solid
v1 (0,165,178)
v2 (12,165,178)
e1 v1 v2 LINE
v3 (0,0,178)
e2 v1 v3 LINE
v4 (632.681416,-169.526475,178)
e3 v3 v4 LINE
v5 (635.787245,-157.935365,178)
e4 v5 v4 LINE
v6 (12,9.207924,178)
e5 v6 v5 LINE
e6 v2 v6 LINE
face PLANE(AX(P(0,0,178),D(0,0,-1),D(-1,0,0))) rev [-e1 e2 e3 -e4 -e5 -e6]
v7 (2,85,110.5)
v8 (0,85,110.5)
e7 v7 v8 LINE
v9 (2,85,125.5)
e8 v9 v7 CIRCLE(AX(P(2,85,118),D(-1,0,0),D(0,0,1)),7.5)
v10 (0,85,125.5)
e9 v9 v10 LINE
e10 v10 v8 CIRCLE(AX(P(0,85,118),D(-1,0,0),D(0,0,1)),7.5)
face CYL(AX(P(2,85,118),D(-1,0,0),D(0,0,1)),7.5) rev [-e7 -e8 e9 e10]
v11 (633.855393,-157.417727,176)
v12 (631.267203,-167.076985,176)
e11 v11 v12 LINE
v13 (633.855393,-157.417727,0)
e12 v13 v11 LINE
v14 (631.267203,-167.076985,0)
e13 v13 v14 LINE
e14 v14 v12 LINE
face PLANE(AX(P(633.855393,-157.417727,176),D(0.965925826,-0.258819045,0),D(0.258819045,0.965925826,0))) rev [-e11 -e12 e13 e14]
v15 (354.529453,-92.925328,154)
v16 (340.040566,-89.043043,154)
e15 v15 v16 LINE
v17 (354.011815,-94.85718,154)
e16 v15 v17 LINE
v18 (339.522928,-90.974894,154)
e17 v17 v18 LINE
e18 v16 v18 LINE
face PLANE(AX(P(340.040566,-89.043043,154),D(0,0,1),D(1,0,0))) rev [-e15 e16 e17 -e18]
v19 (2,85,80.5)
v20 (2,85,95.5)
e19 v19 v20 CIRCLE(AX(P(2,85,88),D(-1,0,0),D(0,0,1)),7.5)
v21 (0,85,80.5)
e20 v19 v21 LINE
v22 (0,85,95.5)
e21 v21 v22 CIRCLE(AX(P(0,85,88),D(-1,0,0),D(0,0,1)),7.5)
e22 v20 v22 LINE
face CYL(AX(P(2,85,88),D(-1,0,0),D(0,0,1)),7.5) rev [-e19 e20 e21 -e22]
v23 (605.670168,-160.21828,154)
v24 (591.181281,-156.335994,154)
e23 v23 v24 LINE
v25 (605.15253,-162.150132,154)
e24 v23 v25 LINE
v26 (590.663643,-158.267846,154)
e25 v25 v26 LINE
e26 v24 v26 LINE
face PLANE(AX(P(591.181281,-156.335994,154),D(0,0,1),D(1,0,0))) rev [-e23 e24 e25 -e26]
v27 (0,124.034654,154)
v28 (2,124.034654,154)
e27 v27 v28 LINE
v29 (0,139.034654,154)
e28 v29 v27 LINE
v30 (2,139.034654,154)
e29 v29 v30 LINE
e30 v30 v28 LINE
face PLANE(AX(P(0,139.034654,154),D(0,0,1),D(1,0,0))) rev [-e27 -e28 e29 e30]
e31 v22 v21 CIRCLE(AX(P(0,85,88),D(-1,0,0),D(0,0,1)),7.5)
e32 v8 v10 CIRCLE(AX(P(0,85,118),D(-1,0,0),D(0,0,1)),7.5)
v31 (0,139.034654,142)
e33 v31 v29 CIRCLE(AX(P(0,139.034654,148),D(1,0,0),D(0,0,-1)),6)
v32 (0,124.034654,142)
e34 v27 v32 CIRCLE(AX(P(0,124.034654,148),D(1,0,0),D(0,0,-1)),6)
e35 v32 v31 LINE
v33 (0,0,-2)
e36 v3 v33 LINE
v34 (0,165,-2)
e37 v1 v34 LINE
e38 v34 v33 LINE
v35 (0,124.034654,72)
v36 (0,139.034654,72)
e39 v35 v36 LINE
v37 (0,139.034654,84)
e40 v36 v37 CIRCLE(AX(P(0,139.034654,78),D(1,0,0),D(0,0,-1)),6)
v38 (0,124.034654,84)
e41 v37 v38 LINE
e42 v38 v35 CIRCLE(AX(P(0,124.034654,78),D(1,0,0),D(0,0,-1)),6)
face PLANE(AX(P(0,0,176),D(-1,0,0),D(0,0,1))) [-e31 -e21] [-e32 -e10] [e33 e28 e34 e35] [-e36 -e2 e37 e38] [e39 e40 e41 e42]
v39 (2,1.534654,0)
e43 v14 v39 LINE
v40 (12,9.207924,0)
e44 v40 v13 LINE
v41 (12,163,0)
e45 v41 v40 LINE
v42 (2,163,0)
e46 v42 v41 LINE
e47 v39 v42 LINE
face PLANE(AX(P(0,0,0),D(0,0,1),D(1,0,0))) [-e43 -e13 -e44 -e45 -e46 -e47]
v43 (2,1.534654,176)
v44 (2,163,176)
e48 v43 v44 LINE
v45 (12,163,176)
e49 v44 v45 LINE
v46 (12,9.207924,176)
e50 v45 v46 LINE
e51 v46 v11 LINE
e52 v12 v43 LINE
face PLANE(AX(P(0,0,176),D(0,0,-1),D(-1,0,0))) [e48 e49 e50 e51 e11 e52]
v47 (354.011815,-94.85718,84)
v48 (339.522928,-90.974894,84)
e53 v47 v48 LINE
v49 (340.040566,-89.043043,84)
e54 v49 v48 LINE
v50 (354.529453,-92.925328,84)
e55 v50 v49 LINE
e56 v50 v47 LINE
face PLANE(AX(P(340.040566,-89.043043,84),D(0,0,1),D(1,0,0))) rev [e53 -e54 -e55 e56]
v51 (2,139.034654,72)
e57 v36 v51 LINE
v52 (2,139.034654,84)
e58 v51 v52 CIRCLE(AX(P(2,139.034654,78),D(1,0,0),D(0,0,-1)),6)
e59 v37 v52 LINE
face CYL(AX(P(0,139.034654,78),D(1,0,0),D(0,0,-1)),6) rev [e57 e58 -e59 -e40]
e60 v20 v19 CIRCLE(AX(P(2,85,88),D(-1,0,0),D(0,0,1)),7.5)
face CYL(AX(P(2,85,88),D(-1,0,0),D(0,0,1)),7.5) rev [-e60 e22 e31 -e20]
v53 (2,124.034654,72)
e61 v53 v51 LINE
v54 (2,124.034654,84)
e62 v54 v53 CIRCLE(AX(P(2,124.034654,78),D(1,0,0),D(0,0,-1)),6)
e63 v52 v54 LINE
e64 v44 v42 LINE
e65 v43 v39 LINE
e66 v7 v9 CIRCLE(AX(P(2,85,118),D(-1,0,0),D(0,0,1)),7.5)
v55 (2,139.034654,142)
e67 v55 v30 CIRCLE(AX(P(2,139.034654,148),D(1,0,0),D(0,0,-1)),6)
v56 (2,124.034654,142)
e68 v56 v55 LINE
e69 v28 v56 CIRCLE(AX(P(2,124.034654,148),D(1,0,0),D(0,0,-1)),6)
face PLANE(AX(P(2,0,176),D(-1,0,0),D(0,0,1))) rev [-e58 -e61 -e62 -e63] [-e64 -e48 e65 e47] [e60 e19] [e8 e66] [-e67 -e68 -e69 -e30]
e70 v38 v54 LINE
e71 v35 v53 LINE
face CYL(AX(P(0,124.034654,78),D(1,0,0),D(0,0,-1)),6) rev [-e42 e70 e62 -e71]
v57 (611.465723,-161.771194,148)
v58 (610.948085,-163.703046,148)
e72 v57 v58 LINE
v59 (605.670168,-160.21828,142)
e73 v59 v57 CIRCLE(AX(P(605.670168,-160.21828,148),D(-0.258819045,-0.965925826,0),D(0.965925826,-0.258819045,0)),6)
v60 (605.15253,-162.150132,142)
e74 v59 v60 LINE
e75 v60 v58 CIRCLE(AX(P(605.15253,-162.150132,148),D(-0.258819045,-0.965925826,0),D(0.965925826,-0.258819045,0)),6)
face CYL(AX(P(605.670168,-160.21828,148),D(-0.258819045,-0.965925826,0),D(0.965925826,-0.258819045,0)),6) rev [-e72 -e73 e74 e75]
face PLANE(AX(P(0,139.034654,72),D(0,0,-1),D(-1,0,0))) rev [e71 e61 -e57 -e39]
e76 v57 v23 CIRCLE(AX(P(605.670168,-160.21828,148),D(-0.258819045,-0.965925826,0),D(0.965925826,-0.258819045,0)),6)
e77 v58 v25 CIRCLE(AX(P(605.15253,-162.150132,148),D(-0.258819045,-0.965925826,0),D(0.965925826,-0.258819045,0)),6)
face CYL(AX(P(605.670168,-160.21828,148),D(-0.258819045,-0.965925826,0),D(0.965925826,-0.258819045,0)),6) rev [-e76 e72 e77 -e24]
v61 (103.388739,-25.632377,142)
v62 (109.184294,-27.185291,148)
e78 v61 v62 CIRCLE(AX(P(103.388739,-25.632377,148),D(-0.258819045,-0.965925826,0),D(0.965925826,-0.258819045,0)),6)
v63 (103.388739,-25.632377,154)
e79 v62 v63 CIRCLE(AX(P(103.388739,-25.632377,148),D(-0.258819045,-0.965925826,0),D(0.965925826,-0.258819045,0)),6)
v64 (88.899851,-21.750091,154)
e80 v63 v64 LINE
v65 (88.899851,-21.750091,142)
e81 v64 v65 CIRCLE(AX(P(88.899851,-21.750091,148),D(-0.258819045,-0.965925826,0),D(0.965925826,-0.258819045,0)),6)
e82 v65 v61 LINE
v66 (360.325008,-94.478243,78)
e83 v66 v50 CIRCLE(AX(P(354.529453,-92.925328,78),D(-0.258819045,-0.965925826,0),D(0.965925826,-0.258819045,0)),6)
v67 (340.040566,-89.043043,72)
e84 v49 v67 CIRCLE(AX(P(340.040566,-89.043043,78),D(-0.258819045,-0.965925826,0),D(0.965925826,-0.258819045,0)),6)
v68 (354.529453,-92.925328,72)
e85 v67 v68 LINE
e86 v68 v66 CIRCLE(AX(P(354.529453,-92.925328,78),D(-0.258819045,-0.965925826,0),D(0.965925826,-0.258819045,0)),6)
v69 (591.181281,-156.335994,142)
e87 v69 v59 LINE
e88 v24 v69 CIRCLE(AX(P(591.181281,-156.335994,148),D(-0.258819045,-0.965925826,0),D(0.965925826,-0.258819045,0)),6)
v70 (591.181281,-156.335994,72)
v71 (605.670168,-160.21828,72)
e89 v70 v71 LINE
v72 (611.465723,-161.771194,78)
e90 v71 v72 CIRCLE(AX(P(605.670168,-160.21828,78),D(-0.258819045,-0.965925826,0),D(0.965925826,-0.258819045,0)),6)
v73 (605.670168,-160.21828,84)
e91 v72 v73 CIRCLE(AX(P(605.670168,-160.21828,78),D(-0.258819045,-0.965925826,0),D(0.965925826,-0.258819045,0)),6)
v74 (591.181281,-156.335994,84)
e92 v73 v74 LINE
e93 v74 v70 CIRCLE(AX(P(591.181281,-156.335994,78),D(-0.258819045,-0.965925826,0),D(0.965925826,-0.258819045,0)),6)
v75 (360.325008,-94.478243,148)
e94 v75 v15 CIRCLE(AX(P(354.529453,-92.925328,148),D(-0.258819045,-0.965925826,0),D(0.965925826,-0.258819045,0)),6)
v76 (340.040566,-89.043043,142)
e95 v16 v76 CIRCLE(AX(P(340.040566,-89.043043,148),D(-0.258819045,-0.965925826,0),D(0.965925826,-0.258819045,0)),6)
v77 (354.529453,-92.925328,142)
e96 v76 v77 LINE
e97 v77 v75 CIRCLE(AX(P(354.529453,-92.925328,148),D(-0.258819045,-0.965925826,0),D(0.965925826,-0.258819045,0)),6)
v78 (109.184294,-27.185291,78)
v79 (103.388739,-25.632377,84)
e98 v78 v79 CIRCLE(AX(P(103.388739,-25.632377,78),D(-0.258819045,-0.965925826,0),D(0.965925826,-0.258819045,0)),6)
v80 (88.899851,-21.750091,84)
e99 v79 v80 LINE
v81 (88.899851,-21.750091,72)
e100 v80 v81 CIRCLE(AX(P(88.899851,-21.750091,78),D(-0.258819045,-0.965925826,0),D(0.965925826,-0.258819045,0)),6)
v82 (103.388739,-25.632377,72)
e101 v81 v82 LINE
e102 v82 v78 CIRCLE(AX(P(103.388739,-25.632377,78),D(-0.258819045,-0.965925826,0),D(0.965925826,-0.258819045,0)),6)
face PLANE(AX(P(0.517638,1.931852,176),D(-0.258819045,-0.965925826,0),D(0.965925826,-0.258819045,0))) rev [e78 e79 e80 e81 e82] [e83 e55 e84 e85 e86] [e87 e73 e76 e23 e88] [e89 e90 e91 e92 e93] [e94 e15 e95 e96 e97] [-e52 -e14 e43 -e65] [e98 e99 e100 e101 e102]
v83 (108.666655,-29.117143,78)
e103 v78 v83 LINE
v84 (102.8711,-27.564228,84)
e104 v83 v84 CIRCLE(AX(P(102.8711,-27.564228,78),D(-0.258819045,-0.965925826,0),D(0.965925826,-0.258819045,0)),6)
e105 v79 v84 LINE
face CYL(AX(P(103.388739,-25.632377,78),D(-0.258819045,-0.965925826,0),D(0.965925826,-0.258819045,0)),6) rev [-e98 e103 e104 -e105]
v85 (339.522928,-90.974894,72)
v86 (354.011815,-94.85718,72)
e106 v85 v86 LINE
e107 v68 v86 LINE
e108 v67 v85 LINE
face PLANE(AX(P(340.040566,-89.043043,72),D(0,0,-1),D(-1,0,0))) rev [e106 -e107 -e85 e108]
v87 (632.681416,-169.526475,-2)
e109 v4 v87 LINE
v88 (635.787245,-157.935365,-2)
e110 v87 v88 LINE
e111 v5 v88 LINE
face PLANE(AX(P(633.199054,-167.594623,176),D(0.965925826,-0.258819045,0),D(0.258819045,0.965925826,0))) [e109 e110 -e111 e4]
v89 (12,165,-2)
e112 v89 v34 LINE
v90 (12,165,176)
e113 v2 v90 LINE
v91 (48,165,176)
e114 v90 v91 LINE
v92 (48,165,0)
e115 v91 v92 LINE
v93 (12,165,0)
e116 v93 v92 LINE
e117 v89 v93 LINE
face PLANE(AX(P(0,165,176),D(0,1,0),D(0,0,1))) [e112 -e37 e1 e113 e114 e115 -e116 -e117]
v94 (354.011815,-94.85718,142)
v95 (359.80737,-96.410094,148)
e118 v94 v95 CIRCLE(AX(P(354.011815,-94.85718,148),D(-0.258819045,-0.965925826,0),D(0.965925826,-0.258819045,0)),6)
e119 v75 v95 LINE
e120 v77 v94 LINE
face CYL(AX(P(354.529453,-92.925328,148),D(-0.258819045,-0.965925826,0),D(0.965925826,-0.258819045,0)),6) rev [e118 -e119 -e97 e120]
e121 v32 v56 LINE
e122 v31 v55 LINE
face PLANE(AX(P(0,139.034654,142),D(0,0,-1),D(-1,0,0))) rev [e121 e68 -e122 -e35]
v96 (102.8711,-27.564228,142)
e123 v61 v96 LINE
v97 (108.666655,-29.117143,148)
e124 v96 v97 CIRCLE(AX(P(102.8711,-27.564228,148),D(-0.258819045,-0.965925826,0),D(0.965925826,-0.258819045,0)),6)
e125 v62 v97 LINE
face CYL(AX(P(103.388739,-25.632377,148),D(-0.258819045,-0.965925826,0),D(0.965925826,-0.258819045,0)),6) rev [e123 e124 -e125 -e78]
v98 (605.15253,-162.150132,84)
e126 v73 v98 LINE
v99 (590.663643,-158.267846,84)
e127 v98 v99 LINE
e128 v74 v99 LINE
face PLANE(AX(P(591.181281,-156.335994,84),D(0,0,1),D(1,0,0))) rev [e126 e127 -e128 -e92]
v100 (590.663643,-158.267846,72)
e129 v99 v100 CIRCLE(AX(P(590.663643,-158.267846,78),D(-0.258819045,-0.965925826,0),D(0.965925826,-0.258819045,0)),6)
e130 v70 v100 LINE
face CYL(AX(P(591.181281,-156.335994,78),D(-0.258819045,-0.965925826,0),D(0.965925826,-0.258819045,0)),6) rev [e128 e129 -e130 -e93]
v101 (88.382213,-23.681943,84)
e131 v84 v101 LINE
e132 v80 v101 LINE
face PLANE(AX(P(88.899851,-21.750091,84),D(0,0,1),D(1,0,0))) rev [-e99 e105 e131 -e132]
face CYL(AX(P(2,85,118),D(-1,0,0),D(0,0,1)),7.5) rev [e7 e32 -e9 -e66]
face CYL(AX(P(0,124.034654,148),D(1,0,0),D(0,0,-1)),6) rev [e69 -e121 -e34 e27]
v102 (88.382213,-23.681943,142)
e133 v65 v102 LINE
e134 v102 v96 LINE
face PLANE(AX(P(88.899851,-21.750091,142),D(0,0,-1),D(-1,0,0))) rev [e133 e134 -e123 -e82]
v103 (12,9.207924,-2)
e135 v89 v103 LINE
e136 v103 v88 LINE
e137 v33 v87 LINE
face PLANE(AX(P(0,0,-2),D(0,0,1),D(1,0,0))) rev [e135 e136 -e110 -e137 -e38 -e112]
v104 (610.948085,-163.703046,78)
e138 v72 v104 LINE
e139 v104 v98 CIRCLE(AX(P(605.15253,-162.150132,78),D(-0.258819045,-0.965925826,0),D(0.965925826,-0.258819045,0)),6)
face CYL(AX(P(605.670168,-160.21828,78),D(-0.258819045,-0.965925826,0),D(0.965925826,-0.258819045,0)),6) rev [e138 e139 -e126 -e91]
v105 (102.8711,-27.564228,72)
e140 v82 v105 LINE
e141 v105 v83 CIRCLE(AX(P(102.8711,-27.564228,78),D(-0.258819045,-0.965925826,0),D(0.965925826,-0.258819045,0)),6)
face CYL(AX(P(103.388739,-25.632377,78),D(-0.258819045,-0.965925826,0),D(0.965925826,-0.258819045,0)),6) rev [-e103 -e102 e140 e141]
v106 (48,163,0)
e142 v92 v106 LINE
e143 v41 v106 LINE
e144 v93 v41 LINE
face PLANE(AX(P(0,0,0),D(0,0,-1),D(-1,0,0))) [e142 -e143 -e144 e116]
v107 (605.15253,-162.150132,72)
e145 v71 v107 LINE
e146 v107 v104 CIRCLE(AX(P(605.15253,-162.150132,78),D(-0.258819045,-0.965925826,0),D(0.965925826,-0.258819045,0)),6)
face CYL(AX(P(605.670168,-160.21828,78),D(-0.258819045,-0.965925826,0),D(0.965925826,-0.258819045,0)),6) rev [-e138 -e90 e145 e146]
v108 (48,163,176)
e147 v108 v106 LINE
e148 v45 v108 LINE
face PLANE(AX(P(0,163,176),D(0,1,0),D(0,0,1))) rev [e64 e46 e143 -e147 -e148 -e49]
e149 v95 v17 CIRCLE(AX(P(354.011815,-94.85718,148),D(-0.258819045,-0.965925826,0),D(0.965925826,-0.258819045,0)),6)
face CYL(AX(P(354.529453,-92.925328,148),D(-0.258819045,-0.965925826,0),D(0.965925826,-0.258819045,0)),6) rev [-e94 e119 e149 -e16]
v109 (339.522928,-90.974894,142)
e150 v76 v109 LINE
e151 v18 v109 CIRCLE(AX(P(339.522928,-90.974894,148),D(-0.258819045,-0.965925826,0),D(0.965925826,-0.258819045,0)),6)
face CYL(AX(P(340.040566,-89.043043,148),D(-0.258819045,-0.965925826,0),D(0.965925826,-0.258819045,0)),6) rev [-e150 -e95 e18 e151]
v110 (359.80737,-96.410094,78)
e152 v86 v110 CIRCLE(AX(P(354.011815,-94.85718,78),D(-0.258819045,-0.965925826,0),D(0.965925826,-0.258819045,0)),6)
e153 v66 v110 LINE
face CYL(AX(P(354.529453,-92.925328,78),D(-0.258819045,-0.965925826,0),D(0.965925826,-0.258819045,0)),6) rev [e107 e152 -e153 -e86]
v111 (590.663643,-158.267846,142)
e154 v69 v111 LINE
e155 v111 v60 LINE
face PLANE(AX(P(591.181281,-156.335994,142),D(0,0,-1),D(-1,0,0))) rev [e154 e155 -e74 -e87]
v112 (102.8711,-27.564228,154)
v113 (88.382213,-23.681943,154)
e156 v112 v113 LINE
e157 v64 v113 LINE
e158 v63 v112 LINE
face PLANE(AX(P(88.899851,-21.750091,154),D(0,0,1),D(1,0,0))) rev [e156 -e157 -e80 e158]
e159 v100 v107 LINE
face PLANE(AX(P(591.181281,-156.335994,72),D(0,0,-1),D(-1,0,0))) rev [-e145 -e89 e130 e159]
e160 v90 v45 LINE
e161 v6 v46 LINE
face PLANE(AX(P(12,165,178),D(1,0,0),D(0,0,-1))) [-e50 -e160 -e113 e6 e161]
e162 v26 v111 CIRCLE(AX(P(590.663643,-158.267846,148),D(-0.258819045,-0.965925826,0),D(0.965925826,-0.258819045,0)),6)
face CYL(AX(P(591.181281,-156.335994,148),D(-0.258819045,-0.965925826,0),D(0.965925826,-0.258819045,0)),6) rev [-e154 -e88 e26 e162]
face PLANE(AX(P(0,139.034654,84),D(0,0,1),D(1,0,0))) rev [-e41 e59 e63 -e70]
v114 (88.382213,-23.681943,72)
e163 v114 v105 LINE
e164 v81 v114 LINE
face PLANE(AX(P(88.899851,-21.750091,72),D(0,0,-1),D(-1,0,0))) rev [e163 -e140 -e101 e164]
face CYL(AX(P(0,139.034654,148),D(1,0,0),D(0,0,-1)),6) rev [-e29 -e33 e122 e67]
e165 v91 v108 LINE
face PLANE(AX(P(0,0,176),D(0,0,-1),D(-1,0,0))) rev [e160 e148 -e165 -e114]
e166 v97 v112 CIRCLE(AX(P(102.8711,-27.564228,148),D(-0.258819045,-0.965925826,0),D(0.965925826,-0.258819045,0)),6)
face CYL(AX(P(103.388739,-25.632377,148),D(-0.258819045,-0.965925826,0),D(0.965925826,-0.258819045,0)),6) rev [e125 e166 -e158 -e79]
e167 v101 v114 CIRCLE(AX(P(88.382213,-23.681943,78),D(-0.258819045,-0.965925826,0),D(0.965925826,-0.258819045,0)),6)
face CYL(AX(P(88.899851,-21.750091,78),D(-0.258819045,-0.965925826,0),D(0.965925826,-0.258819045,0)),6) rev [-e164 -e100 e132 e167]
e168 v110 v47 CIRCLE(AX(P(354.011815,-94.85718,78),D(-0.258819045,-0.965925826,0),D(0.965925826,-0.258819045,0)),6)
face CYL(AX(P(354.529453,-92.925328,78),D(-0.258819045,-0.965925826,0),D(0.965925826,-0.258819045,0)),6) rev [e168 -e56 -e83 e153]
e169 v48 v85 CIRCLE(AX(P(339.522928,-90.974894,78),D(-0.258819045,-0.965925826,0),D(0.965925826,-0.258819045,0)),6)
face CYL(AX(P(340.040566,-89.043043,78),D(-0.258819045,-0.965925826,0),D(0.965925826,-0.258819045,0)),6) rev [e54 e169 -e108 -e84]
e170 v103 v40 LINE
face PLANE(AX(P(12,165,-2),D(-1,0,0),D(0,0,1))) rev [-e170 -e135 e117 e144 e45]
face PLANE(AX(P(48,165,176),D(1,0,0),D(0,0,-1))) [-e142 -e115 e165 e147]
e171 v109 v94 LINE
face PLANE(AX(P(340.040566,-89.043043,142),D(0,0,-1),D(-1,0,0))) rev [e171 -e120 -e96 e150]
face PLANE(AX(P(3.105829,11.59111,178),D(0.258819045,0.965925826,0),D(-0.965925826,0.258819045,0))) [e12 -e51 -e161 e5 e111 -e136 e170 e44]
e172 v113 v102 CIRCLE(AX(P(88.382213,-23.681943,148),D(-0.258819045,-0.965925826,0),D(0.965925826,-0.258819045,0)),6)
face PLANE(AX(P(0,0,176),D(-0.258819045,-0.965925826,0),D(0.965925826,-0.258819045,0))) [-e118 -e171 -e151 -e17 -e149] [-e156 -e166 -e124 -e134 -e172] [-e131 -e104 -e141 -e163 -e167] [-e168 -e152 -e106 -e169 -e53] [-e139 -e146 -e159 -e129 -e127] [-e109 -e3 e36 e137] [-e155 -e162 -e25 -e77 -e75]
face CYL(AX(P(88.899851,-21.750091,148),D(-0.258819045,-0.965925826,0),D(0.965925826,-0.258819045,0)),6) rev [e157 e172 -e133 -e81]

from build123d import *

# Parameters (mm, degrees)
EXTRUDE_THIN1_DEPTH  = 176
EXTRUDE_THIN2_DEPTH  = 2
EXTRUDE_THIN3_DEPTH  = 2
SKETCH4_W            = 2
SKETCH4_H            = 176
BOSS_EXTRUDE1_DEPTH  = 10
CUT_EXTRUDE1_DEPTH   = 2
CUT_EXTRUDE2_DEPTH   = 2
SKETCH7_R            = 7.5
CUT_EXTRUDE3_DEPTH   = 2
LPATTERN3_COUNT      = 2
LPATTERN3_PITCH      = 30
LPATTERN4_COUNT      = 2
LPATTERN4_PITCH      = 70
LPATTERN4_COUNT_DIR2 = 3
LPATTERN4_PITCH_DIR2 = 260
LPATTERN5_COUNT      = 2
LPATTERN5_PITCH      = 70


with BuildPart() as part:
    # Sketch1 → Extrude-Thin1 (new body)
    with BuildSketch(Plane.XY):
        Polygon((632.681416219, -169.526474542), (0, 0), (0, 165), (48, 165), (48, 163), (2, 163), (2, 1.534653976), (633.19905431, -167.59462289), align=None)
    extrude(amount=EXTRUDE_THIN1_DEPTH)

    # Sketch2 → Extrude-Thin2 (add)
    with BuildSketch(Plane.XY.offset(176)):
        Polygon((0, 165), (0, 0), (632.681416219, -169.526474542), (635.787244761, -157.935364627), (12, 9.207923856), (12, 165), align=None)
    extrude(amount=EXTRUDE_THIN2_DEPTH)

    # Sketch3 → Extrude-Thin3 (add)
    with BuildSketch(Plane(origin=(0, 0, 0), x_dir=(-1, 0, 0), z_dir=(0, 0, -1))):
        Polygon((0, 165), (0, 0), (-632.681416219, -169.526474542), (-635.787244761, -157.935364627), (-12, 9.207923856), (-12, 165), align=None)
    extrude(amount=EXTRUDE_THIN3_DEPTH)

    # Sketch4 → Boss-Extrude1 (add)
    with BuildSketch(Plane(origin=(0.51763809, 1.931851653, 0), x_dir=(0.9659258262890673, -0.25881904510252474, 0), z_dir=(0.25881904510252474, 0.9659258262890673, 0))):
        with Locations((654, -88)):
            Rectangle(SKETCH4_W, SKETCH4_H)
    extrude(amount=BOSS_EXTRUDE1_DEPTH)

    # Sketch5 → Cut-Extrude1 (cut)
    with BuildSketch(Plane(origin=(0, 0, 0), x_dir=(0.9659258262890673, -0.2588190451025247, 0), z_dir=(-0.2588190451025247, -0.9659258262890673, 0))):
        with BuildLine():
            Line((611.5, 154), (626.5, 154))
            ThreePointArc((626.5, 154), (632.5, 148), (626.5, 142))
            Line((626.5, 142), (611.5, 142))
            ThreePointArc((611.5, 142), (605.5, 148), (611.5, 154))
        make_face()
    cut_extrude1 = extrude(amount=-CUT_EXTRUDE1_DEPTH, mode=Mode.SUBTRACT)

    # Sketch6 → Cut-Extrude2 (cut)
    with BuildSketch(Plane(origin=(2, 0, 0), x_dir=(0, 0, -1), z_dir=(1, 0, 0))):
        with BuildLine():
            Line((-142, 139.034653976), (-142, 124.034653976))
            ThreePointArc((-142, 124.034653976), (-148, 118.034653976), (-154, 124.034653976))
            Line((-154, 124.034653976), (-154, 139.034653976))
            ThreePointArc((-154, 139.034653976), (-148, 145.034653976), (-142, 139.034653976))
        make_face()
    cut_extrude2 = extrude(amount=-CUT_EXTRUDE2_DEPTH, mode=Mode.SUBTRACT)

    # Sketch7 → Cut-Extrude3 (cut)
    with BuildSketch(Plane.ZY):
        with Locations((88, 85)):
            Circle(SKETCH7_R)
    cut_extrude3 = extrude(amount=-CUT_EXTRUDE3_DEPTH, mode=Mode.SUBTRACT)

    # LPattern3: Cut-Extrude3 ×2
    with Locations(*[(0, 0, i * LPATTERN3_PITCH) for i in range(1, LPATTERN3_COUNT)]):
        add(cut_extrude3, mode=Mode.SUBTRACT)

    # LPattern4: Cut-Extrude1 2 × 3
    with Locations(*[Vector(0, 0, -1) * (i * LPATTERN4_PITCH) + Vector(-0.9659258262890673, 0.2588190451025247, 0) * (j * LPATTERN4_PITCH_DIR2) for i in range(LPATTERN4_COUNT) for j in range(LPATTERN4_COUNT_DIR2) if (i, j) != (0, 0)]):
        add(cut_extrude1, mode=Mode.SUBTRACT)

    # LPattern5: Cut-Extrude2 ×2
    with Locations(*[(0, 0, -i * LPATTERN5_PITCH) for i in range(1, LPATTERN5_COUNT)]):
        add(cut_extrude2, mode=Mode.SUBTRACT)


solid = part.part
